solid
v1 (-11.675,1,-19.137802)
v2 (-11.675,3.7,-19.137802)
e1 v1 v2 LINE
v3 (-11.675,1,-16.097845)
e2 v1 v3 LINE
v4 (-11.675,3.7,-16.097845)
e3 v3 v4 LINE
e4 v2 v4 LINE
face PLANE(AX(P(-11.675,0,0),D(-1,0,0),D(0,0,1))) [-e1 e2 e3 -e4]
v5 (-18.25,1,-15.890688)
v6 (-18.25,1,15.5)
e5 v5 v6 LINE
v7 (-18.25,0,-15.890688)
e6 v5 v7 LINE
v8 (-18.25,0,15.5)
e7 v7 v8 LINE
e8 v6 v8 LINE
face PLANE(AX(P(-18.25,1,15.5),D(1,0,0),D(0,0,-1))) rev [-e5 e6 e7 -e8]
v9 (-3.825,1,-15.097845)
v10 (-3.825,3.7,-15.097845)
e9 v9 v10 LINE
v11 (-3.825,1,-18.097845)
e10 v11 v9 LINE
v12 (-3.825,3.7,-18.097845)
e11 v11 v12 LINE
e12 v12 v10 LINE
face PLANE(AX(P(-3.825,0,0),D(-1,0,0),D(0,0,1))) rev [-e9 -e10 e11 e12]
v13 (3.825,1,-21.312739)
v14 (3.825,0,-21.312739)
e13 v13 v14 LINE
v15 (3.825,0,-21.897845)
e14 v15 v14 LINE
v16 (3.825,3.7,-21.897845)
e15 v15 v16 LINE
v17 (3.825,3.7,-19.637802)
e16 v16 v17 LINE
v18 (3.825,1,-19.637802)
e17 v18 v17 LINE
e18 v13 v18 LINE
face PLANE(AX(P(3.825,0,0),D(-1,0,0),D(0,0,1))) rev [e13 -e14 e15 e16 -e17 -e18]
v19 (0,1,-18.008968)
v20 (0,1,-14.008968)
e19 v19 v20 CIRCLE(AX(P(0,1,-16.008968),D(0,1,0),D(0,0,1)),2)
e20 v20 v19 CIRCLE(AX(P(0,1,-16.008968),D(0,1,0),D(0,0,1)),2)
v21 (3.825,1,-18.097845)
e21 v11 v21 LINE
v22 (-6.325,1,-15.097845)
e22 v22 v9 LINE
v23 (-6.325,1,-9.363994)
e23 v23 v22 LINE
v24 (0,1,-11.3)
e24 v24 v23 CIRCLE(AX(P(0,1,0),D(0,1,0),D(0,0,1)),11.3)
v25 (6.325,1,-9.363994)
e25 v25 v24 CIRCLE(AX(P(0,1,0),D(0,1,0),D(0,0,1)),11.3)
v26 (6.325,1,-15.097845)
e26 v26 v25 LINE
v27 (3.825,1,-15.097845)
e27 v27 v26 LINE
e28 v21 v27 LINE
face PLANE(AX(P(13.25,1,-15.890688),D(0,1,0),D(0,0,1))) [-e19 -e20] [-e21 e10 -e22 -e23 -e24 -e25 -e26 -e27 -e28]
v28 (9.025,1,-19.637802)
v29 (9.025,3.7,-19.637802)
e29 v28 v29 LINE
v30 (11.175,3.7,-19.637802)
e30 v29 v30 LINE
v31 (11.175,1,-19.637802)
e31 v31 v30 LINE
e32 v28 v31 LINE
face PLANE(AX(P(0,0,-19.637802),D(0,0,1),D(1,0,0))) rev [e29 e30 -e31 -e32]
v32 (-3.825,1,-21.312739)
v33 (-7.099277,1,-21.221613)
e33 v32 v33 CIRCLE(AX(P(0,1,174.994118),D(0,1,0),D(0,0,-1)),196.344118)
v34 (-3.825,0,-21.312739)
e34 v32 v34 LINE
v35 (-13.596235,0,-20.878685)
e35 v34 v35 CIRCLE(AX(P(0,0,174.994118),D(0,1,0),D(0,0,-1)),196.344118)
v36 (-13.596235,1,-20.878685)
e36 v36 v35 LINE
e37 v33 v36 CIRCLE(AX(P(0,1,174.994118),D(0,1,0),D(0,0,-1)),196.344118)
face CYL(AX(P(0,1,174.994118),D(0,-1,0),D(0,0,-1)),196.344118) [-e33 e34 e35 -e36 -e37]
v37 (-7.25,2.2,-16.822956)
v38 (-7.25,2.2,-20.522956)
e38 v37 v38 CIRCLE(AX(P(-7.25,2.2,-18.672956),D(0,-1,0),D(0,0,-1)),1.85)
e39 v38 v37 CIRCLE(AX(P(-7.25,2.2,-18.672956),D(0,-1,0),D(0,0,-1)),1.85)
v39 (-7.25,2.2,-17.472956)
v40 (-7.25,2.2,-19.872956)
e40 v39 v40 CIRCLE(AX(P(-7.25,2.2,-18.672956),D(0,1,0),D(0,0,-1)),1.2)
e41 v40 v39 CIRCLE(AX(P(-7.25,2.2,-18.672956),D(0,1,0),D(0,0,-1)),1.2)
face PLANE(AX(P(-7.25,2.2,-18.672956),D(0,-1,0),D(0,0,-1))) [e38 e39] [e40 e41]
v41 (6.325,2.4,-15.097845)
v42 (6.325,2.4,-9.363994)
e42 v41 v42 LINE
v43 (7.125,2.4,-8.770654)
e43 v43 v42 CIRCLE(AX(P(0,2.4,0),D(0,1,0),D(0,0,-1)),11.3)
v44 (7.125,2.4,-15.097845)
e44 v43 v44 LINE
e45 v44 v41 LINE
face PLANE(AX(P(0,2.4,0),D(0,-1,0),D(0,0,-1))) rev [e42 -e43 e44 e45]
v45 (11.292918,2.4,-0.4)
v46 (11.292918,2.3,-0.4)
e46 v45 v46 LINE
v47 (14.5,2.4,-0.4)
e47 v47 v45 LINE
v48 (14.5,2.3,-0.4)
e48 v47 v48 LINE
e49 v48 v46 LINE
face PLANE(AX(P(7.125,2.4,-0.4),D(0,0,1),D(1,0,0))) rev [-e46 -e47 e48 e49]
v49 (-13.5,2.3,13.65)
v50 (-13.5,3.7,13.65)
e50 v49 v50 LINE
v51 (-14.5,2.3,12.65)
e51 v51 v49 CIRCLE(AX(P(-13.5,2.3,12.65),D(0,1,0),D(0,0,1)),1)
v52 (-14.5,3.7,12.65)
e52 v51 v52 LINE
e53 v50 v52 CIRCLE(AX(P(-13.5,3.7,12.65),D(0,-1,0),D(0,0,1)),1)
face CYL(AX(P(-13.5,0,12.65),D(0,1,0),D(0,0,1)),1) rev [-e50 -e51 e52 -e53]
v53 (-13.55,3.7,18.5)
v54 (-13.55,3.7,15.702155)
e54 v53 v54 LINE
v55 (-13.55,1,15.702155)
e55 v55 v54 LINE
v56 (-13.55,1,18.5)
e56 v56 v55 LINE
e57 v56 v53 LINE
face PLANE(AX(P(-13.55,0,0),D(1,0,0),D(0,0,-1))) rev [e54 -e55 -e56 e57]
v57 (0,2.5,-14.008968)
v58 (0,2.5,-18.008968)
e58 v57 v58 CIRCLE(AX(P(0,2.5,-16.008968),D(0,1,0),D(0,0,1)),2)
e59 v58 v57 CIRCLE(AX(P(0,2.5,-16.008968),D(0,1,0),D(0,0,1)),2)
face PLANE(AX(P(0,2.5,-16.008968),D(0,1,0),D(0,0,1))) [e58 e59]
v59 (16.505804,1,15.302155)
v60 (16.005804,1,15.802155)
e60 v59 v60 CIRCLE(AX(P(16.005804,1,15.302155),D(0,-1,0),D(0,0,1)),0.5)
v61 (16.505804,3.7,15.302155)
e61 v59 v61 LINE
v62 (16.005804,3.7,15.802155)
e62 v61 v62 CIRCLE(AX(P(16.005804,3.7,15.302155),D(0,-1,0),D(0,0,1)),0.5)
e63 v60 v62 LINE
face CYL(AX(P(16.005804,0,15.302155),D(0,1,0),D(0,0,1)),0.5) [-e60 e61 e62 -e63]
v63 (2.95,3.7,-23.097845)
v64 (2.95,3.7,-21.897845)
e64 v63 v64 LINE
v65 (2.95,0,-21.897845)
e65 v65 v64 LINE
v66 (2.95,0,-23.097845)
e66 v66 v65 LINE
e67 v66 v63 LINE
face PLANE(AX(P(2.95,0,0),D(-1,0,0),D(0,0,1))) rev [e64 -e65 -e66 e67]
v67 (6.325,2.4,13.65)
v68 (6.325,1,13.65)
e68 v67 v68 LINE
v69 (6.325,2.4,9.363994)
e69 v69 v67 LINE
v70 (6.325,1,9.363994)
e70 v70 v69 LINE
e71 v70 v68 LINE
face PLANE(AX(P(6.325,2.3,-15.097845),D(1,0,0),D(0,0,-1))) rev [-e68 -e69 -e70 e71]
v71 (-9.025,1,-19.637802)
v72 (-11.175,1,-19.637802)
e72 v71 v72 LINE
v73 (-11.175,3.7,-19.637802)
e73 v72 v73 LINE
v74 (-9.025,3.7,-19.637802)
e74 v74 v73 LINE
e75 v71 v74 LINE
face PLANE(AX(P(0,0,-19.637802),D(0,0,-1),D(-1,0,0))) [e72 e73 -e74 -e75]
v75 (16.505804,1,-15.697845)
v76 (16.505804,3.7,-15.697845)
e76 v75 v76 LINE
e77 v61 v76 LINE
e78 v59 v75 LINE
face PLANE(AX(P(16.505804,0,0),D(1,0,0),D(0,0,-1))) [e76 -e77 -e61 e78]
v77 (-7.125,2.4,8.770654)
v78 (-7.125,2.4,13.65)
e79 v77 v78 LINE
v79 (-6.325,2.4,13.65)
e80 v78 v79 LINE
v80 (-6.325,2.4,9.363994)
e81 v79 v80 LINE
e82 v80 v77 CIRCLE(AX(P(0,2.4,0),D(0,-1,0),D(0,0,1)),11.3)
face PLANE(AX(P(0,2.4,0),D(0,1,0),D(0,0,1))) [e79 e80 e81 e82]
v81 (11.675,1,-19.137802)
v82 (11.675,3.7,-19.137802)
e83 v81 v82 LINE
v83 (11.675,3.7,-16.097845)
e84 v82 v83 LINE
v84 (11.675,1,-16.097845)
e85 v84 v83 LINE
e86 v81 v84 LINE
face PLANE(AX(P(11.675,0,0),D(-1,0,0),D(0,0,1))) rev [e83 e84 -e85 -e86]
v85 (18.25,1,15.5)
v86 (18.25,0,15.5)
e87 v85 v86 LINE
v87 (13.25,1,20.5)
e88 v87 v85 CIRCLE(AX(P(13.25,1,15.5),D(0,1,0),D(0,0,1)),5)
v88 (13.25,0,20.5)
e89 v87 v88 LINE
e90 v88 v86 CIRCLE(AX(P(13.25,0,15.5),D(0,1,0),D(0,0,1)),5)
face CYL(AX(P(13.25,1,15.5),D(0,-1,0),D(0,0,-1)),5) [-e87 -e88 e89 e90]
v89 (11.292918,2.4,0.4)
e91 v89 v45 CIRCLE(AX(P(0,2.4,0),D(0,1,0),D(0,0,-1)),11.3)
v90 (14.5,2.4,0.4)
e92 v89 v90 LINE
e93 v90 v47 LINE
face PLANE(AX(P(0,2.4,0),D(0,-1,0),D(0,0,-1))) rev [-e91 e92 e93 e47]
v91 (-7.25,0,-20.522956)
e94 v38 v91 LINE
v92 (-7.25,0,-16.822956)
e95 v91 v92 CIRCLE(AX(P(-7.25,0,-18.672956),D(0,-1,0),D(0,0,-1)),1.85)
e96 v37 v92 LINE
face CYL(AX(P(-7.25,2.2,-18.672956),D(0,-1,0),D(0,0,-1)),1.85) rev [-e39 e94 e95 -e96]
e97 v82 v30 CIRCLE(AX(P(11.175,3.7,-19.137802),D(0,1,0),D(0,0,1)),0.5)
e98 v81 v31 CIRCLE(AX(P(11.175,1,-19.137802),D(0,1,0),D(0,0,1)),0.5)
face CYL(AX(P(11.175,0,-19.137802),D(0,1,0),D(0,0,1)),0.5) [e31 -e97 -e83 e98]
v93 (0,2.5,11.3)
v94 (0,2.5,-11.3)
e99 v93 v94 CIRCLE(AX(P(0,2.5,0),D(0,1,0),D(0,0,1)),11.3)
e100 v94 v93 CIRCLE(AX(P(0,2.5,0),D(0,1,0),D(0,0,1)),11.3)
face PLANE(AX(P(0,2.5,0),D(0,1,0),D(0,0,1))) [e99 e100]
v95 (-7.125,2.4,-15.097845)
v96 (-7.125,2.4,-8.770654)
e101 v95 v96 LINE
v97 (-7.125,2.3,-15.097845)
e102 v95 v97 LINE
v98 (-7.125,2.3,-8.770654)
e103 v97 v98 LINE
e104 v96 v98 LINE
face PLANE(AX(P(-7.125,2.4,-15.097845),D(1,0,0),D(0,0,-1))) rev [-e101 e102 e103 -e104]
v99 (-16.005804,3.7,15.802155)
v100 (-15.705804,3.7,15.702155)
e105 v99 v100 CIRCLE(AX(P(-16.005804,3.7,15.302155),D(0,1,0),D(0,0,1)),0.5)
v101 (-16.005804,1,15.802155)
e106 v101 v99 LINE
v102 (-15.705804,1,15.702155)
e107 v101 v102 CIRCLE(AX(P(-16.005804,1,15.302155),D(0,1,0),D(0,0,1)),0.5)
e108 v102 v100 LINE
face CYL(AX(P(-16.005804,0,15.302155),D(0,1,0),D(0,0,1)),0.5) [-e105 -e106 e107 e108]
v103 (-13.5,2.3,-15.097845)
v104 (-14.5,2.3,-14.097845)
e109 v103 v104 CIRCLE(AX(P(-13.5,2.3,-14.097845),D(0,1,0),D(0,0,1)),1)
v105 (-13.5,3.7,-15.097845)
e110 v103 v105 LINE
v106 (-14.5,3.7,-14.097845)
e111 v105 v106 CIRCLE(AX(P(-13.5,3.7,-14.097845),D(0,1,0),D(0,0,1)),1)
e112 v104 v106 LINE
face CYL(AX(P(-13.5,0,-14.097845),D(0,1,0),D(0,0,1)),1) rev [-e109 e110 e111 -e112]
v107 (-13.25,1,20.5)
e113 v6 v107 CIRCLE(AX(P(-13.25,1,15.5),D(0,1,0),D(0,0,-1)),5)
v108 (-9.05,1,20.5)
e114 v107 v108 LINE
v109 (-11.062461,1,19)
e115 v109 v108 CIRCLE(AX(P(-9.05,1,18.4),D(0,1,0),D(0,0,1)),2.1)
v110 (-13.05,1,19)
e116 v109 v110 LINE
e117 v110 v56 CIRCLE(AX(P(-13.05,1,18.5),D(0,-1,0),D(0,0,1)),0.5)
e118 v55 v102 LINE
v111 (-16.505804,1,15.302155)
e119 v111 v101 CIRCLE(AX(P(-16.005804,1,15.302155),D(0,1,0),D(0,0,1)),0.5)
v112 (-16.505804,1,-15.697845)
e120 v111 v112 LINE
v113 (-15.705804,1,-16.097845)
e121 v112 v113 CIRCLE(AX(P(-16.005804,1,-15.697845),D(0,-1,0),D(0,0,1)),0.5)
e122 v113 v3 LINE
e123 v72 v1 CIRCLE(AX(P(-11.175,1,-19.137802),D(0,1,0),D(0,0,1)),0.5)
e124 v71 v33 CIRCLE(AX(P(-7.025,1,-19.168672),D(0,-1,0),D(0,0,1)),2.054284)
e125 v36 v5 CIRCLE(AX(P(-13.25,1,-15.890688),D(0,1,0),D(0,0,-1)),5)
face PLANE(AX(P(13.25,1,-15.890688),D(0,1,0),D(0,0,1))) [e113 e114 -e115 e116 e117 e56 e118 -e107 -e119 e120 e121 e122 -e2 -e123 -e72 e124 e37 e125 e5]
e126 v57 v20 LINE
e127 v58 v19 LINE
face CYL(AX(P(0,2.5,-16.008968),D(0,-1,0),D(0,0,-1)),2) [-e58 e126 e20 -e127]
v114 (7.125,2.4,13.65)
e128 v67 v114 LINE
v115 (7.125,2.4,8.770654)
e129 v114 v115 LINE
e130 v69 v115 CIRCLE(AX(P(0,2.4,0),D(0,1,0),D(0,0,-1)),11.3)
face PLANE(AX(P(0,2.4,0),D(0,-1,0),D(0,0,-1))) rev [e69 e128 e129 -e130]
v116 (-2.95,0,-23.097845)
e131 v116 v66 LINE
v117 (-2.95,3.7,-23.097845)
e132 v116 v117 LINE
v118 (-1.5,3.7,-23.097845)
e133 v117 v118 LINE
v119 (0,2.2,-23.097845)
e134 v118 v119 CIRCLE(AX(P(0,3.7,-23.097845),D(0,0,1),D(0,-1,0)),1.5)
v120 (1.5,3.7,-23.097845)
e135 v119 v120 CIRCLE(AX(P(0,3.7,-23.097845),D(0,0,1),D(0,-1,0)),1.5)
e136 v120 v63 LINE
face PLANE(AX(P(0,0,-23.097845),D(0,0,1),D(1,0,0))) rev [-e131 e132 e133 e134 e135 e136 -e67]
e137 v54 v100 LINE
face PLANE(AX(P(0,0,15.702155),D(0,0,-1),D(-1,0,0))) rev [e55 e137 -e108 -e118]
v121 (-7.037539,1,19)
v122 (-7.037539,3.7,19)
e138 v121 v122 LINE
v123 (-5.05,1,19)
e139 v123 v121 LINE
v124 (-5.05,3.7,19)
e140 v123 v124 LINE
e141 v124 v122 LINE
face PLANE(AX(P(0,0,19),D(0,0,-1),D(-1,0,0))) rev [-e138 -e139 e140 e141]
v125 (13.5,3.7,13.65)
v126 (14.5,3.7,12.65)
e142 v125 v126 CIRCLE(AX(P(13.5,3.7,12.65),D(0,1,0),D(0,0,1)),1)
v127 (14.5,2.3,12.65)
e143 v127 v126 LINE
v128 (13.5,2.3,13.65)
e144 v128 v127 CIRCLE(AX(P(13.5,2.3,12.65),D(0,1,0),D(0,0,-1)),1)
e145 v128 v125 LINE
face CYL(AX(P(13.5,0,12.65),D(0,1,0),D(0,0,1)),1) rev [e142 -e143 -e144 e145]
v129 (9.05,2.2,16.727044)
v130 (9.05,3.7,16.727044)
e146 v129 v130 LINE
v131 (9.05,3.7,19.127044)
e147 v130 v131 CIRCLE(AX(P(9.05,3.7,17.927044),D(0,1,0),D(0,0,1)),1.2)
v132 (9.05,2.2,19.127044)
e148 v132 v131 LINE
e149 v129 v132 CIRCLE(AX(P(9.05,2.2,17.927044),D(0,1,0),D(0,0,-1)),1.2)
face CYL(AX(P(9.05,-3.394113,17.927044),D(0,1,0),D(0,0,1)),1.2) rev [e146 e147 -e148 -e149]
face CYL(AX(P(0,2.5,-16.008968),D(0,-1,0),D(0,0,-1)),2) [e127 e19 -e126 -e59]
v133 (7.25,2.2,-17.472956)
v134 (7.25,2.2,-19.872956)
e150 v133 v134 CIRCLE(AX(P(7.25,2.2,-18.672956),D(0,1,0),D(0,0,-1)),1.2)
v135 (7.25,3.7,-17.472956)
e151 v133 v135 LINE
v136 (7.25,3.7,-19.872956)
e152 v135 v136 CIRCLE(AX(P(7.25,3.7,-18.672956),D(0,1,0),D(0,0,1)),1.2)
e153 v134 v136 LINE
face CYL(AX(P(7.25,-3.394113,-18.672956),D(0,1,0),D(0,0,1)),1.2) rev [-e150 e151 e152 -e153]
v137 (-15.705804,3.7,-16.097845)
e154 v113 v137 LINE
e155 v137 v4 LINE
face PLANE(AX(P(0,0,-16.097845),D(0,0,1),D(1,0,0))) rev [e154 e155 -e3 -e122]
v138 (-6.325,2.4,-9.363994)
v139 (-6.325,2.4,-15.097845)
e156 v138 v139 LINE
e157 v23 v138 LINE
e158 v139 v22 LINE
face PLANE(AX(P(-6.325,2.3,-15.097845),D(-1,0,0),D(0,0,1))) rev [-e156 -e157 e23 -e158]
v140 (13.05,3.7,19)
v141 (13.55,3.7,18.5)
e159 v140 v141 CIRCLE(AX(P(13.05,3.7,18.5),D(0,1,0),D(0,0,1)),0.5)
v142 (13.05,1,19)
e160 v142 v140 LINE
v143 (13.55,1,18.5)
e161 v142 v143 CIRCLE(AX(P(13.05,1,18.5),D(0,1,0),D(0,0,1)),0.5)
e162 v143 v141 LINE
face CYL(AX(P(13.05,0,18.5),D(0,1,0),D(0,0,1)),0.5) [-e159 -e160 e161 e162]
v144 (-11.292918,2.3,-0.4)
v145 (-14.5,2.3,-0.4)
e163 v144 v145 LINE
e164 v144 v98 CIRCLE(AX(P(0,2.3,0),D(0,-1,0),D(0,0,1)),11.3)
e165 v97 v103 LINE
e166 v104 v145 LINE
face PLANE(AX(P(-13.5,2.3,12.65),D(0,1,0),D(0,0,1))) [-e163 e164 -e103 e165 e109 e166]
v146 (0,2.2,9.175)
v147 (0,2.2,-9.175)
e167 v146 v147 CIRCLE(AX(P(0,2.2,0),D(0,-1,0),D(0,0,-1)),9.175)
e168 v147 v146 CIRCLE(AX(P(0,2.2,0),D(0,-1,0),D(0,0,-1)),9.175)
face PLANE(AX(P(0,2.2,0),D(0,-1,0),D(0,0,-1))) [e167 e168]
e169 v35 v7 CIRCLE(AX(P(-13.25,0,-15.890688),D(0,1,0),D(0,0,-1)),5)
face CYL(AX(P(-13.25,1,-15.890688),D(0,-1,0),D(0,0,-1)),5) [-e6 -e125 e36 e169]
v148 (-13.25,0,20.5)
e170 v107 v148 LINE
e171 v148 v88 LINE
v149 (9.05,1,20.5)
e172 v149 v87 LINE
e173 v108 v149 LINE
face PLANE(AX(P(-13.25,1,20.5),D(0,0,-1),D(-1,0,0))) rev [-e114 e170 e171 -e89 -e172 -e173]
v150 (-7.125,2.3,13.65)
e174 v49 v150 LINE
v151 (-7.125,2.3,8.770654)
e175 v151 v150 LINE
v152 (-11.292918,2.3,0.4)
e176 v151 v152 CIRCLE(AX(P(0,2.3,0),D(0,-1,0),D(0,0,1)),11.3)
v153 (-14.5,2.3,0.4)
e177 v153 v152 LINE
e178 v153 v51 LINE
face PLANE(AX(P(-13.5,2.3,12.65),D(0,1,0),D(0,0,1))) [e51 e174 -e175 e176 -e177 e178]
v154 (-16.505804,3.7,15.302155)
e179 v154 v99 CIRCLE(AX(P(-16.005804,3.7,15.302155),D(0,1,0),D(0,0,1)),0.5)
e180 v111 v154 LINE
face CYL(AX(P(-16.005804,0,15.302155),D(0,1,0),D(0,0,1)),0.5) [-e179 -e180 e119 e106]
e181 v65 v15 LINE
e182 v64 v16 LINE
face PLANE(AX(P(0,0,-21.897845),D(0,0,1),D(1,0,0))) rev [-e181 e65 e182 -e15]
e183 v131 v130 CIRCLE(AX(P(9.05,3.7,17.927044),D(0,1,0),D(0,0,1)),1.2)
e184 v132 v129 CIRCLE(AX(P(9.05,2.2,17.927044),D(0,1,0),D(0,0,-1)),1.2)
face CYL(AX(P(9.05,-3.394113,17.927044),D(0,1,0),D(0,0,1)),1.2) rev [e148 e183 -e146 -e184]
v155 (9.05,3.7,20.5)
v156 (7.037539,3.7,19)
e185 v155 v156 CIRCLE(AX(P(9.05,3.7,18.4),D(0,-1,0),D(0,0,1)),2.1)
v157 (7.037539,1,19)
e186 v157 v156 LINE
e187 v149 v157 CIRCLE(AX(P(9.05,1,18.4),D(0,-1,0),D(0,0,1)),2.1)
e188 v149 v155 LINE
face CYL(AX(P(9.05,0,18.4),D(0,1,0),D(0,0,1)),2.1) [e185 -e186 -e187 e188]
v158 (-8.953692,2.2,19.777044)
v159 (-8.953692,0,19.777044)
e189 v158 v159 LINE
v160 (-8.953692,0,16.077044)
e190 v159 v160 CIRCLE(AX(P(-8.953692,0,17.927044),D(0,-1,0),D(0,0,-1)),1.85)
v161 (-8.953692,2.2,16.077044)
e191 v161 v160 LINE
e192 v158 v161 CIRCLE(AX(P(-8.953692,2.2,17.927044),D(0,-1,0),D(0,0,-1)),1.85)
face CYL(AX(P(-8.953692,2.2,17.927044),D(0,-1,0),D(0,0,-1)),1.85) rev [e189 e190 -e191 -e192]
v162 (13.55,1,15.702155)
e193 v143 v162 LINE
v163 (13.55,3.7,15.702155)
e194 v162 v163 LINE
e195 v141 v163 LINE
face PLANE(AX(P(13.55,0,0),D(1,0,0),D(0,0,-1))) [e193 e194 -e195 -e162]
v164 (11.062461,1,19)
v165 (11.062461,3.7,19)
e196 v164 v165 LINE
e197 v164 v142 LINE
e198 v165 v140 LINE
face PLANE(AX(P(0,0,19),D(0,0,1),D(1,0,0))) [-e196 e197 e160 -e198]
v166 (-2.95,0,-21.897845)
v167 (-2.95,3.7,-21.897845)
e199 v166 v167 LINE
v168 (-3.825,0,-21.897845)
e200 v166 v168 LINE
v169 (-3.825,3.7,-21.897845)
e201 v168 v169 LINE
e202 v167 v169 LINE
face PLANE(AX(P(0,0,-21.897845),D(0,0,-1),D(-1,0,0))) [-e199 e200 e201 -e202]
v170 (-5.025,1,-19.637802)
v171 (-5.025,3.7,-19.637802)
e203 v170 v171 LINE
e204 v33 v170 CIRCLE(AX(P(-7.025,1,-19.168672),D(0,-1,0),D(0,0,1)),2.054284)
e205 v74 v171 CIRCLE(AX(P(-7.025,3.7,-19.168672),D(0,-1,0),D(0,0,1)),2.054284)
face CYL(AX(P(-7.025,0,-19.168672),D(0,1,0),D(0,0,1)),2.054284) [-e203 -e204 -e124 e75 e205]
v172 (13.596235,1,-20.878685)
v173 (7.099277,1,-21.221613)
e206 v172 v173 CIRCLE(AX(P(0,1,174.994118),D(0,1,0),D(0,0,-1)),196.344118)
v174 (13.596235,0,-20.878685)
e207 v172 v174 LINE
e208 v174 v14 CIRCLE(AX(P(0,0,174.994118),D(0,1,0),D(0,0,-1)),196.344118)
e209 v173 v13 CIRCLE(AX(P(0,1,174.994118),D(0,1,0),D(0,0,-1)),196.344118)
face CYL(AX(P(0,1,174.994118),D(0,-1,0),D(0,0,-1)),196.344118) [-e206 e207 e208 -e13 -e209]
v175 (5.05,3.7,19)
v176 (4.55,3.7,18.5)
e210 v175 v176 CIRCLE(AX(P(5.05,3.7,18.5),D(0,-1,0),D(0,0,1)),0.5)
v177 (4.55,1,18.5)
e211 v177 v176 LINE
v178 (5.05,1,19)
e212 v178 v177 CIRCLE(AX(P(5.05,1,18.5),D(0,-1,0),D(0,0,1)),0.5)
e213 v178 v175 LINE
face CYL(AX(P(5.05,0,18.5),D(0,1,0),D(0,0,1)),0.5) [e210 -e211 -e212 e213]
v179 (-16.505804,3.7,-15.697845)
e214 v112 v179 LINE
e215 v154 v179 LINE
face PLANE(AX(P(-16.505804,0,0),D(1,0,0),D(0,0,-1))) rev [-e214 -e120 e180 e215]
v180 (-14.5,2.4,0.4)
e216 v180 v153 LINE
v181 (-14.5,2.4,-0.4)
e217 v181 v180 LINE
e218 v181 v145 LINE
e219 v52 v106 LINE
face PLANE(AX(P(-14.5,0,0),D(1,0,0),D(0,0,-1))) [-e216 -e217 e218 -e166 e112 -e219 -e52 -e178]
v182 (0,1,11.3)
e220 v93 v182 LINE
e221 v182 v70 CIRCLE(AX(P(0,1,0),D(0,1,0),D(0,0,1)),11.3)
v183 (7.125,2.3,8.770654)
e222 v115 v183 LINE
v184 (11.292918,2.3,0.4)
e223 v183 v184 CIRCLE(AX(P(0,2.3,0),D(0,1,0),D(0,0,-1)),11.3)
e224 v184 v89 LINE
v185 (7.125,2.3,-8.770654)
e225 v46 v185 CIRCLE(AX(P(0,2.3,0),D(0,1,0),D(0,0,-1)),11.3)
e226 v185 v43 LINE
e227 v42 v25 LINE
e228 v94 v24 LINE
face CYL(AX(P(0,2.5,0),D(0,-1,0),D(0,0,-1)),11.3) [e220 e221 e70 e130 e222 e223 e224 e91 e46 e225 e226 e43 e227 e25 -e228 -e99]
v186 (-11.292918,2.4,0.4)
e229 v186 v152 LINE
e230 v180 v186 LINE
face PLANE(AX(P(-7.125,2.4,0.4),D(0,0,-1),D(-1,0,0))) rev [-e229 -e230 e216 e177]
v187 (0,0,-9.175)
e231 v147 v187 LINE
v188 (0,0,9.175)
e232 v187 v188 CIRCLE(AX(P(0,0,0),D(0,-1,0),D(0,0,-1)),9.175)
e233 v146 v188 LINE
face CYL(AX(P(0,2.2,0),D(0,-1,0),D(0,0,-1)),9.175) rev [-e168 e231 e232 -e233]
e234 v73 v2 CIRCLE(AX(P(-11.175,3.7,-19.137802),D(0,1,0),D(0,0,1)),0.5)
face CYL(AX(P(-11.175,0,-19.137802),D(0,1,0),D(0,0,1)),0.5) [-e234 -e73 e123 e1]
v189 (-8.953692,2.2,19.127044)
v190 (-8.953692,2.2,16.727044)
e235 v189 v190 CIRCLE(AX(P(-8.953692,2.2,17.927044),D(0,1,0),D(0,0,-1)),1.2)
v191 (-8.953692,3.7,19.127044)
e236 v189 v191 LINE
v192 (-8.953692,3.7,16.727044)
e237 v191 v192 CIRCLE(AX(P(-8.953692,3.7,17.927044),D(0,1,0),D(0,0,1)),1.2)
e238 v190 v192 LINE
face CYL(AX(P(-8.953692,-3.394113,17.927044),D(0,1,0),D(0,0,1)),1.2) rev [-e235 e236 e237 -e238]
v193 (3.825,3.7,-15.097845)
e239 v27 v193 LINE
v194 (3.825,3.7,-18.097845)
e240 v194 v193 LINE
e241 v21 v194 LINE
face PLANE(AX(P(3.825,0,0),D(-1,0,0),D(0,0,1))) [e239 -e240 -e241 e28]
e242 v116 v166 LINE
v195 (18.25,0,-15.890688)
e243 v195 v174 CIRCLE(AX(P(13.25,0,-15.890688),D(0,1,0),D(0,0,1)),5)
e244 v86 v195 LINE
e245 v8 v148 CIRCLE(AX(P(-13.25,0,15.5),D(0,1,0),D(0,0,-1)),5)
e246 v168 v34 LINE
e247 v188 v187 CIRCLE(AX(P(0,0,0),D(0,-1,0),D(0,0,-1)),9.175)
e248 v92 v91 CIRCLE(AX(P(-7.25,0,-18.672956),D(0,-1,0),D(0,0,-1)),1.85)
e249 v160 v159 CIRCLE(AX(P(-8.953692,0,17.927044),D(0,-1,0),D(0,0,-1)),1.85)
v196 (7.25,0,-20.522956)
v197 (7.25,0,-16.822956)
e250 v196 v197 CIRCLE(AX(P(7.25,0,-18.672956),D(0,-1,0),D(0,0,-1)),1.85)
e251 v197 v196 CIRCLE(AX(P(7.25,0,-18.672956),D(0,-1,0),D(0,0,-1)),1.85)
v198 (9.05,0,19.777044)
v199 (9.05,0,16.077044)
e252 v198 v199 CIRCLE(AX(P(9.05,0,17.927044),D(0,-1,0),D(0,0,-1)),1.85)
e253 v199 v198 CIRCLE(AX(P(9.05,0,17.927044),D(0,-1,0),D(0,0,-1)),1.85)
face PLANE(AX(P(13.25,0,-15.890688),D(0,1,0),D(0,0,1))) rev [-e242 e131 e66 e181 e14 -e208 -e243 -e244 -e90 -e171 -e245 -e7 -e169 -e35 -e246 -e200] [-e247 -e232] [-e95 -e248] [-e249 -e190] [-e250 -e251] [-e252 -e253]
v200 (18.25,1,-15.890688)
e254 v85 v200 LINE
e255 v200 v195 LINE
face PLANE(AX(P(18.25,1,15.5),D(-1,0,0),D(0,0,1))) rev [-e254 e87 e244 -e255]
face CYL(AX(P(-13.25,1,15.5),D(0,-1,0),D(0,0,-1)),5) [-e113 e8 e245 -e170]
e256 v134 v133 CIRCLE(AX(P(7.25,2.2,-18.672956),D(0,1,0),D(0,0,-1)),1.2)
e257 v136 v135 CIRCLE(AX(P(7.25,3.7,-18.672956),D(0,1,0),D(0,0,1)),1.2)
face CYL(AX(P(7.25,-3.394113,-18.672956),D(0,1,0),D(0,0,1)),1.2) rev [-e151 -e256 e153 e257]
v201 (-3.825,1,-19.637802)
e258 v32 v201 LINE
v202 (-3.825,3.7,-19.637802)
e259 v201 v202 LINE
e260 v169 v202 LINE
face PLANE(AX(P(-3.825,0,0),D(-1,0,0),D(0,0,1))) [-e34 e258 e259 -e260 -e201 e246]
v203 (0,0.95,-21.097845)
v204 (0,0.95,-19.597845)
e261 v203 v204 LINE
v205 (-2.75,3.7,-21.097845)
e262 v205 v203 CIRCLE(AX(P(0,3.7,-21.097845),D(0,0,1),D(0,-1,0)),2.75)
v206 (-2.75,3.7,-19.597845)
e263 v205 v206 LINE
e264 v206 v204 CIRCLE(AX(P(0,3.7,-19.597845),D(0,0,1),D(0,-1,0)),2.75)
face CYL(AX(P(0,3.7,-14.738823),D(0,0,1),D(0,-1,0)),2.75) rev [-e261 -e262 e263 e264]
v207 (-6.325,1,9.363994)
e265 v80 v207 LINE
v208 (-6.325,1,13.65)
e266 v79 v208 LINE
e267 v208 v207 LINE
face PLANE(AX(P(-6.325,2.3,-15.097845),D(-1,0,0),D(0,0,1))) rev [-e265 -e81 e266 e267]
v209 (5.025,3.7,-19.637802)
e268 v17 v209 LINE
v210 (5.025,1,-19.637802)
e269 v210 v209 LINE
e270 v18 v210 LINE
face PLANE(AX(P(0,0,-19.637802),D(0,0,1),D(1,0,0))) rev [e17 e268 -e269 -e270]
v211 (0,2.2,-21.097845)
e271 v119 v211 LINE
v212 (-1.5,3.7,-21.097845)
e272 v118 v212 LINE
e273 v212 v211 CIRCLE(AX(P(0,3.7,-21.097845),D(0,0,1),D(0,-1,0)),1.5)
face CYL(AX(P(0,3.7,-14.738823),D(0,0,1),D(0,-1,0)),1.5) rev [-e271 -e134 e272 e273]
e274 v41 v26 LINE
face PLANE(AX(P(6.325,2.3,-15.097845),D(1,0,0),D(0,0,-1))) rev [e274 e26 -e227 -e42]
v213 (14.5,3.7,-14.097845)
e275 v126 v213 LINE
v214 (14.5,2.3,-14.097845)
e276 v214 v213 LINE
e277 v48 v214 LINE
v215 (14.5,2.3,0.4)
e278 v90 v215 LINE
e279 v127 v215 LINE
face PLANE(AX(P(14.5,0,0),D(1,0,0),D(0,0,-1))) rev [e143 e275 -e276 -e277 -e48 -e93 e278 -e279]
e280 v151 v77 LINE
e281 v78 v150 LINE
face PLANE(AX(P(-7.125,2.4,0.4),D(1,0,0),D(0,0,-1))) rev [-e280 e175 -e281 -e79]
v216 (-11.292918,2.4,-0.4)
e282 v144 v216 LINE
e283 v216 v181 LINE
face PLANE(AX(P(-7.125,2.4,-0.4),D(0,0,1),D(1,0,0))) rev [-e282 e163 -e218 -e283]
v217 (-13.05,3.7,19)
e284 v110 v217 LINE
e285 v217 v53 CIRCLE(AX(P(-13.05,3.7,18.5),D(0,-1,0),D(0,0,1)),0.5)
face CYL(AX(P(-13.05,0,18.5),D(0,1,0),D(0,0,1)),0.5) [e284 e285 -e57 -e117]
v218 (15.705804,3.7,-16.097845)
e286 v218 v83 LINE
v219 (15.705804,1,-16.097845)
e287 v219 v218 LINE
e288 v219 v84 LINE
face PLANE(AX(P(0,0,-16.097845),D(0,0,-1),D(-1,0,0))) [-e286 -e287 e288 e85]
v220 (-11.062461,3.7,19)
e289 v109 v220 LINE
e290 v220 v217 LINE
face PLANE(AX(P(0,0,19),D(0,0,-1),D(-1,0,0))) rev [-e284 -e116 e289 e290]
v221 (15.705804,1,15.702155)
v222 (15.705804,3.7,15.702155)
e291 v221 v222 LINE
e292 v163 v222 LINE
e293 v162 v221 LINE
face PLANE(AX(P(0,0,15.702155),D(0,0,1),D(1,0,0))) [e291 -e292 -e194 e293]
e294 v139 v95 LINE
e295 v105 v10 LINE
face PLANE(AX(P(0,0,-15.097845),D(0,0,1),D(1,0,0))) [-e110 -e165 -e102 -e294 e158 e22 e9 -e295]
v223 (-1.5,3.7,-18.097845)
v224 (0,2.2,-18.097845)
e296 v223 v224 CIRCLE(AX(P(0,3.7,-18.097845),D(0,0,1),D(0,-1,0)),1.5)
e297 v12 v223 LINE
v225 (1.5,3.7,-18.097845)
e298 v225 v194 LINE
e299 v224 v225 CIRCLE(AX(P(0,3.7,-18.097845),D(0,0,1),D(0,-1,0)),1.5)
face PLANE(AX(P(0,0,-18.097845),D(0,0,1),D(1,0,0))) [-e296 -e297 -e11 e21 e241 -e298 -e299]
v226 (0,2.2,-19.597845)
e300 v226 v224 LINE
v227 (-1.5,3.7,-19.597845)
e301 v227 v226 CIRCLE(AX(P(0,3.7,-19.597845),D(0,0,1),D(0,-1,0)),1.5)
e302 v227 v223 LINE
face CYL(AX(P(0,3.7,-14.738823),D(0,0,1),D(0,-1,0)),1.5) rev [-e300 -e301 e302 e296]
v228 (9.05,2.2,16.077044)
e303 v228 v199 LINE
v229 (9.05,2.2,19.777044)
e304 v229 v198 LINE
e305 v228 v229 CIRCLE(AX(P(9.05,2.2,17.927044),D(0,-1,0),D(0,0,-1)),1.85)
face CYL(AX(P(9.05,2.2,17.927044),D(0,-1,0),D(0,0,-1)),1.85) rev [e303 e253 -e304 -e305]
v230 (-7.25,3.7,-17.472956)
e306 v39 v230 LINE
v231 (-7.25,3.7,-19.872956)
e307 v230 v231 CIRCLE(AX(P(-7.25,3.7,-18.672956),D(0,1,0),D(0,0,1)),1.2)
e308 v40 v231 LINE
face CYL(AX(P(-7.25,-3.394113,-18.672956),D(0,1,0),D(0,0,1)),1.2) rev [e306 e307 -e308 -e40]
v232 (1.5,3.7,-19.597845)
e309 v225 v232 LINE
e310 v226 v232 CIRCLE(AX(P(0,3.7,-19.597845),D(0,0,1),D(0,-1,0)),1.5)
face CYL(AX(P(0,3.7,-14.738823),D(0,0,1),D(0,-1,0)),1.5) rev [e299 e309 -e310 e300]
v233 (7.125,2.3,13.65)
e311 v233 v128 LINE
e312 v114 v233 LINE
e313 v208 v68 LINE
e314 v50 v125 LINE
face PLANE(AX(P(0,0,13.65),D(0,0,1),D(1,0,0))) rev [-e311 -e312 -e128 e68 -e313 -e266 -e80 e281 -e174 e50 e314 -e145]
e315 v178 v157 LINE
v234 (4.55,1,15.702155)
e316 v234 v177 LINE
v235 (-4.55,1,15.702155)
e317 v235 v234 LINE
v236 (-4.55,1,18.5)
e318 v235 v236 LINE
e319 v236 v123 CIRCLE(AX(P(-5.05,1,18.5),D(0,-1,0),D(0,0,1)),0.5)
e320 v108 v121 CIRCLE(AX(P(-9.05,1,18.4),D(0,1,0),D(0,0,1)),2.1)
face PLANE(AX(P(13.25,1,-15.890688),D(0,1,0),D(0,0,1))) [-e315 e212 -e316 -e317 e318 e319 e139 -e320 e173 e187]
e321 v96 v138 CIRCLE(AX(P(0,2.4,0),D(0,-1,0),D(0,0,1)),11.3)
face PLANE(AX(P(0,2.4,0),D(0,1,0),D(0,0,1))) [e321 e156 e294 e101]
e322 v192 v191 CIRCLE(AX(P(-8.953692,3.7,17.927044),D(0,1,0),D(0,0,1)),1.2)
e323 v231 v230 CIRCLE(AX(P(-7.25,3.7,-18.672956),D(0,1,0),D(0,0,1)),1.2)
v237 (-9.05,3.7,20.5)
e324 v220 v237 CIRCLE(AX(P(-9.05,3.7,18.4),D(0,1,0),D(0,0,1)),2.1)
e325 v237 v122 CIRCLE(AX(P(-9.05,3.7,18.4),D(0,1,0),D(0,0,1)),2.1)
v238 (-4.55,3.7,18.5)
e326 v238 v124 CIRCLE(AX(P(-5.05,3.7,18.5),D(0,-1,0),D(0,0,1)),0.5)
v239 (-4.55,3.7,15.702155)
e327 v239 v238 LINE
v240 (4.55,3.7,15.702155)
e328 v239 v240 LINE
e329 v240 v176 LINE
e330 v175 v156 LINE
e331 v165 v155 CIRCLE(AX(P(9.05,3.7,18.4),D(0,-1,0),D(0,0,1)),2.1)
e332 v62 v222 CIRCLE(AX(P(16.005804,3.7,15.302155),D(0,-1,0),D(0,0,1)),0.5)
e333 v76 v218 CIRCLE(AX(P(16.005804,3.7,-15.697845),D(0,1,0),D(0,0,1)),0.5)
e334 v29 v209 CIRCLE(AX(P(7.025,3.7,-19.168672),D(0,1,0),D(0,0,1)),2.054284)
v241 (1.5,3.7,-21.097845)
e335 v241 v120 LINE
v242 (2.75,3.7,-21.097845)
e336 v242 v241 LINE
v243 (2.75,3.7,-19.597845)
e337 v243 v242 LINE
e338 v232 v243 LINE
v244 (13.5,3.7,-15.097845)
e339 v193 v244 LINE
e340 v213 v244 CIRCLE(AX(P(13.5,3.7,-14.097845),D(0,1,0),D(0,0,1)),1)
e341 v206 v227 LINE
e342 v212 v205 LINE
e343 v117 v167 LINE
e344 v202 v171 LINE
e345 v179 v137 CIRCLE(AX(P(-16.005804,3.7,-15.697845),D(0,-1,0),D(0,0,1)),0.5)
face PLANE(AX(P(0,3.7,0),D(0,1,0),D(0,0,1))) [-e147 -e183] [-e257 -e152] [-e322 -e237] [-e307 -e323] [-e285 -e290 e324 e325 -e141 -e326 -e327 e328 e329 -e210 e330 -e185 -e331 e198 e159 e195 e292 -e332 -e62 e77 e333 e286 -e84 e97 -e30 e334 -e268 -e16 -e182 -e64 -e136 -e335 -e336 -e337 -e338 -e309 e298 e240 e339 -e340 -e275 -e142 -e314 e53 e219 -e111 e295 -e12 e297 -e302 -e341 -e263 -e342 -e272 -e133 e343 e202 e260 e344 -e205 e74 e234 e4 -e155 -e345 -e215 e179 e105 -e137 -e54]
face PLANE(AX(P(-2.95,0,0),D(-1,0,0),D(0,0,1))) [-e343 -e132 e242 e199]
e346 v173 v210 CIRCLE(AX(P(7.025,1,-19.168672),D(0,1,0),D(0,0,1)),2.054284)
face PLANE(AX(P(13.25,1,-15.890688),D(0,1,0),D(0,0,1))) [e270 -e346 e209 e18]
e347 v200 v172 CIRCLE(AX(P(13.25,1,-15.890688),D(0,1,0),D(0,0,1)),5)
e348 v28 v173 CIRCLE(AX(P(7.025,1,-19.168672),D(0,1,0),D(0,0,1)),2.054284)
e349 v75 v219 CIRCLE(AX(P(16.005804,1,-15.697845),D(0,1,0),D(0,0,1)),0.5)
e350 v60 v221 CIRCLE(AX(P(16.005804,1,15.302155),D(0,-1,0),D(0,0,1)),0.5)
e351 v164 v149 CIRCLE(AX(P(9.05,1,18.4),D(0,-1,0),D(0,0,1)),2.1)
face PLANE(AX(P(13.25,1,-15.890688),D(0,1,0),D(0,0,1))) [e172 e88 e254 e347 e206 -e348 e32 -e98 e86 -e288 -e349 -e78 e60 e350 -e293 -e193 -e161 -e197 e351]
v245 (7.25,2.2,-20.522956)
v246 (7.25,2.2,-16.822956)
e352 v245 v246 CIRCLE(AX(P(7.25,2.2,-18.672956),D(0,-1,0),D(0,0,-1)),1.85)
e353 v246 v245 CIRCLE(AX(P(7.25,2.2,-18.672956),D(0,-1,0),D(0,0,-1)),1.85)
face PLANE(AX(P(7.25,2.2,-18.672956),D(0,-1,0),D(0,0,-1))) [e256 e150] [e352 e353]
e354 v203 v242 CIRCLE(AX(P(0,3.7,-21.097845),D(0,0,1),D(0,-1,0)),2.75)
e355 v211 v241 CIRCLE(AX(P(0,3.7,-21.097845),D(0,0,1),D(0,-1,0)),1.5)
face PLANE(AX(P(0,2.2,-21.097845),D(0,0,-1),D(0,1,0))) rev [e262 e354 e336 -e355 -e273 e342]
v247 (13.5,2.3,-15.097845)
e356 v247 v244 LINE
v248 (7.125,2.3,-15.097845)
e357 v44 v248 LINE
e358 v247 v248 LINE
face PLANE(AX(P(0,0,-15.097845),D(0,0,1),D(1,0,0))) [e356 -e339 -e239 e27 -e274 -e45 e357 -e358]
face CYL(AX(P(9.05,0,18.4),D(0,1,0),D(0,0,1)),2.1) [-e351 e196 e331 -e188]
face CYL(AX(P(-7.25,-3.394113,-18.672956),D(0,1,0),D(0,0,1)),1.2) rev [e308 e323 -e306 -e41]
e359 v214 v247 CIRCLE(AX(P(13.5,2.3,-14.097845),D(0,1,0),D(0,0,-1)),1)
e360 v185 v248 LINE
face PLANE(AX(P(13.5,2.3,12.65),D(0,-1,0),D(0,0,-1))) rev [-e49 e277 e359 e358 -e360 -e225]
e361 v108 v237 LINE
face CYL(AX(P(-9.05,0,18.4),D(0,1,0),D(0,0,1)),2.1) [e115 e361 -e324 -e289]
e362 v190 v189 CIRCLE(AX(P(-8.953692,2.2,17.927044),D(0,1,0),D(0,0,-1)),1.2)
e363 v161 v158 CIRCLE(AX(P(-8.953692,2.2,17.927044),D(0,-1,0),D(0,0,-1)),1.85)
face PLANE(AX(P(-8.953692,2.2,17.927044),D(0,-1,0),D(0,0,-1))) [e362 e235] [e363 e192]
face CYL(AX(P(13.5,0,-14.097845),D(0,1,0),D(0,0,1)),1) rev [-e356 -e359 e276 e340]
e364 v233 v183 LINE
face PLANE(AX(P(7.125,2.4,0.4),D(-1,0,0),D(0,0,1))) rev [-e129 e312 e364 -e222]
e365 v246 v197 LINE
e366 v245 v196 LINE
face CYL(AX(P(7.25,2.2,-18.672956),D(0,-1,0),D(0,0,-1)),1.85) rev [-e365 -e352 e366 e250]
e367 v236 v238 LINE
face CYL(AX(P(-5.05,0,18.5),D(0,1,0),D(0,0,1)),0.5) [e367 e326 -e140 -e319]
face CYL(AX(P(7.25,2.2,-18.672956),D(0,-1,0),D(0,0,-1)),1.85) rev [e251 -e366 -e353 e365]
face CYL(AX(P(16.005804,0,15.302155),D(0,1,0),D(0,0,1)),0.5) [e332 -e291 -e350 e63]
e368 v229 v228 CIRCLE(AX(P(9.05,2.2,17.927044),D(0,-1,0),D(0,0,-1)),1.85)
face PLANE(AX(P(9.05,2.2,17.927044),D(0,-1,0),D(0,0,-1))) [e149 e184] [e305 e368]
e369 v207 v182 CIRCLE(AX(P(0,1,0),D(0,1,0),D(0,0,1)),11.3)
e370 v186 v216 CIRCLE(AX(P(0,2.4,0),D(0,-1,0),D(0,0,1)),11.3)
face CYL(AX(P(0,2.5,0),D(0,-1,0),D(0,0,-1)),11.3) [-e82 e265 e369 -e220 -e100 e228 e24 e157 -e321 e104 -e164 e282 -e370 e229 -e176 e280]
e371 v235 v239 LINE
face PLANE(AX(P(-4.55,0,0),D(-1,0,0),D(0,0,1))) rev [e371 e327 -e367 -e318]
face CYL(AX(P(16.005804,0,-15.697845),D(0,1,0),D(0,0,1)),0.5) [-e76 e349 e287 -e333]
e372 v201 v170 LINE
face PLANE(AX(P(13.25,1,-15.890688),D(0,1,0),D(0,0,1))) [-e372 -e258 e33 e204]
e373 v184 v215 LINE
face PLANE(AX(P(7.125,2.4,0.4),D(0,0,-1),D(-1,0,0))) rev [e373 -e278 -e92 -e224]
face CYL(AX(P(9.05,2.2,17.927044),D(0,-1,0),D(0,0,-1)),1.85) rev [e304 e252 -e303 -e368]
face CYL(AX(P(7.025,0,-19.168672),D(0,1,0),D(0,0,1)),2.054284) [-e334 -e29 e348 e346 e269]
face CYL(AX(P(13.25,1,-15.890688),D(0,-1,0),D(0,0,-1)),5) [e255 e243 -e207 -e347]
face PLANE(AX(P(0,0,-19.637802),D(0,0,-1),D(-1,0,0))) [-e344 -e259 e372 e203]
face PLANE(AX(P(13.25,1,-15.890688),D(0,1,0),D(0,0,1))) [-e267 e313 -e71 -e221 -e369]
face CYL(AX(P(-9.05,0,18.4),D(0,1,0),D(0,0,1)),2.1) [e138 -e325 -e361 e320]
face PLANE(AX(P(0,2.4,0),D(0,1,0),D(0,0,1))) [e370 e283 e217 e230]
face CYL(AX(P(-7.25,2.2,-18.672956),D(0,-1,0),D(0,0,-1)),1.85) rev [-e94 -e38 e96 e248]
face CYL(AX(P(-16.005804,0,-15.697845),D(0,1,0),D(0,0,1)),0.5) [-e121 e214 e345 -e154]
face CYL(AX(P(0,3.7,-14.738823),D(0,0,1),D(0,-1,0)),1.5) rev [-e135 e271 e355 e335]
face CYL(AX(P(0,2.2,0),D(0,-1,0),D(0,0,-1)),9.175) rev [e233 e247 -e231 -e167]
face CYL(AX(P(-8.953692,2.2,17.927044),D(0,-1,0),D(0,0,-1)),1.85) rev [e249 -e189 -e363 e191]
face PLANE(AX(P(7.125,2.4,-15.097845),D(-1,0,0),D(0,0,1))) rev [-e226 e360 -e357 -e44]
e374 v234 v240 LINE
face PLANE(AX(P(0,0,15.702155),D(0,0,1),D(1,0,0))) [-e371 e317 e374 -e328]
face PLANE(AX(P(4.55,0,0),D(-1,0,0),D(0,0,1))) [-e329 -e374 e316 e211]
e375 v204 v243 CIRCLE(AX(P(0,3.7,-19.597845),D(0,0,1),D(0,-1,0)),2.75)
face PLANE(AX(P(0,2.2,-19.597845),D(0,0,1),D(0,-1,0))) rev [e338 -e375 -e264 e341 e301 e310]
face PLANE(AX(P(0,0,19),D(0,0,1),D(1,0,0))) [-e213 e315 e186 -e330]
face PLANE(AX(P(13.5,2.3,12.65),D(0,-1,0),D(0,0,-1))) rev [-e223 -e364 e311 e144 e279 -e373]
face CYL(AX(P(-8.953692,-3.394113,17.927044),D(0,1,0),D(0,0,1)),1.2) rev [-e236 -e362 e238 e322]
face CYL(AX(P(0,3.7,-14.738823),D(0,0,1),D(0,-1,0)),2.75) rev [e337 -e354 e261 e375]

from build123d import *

# Parameters (mm, degrees)
BOSS_EXTRUDE1_DEPTH      = 1
BOSS_EXTRUDE3_DEPTH      = 2.7
BOSS_EXTRUDE3_DEPTH_BACK = 1
BOSS_EXTRUDE4_DEPTH      = 1.3
BOSS_EXTRUDE5_DEPTH      = 0.1
SKETCH_6_R               = 11.3
BOSS_EXTRUDE6_DEPTH      = 1.5
SKETCH_8_R               = 1.2
CUT_EXTRUDE1_DEPTH       = 3.7
SKETCH_9_R               = 1.85
SKETCH_9_R_2             = 9.175
CUT_EXTRUDE2_DEPTH       = 2.2
SKETCH_10_R              = 2
BOSS_EXTRUDE11_DEPTH     = 1.5


with BuildPart() as part:
    # Sketch 1 → Boss-Extrude1 (new body)
    with BuildSketch(Plane(origin=(0, 0, 0), x_dir=(1, 0, 0), z_dir=(0, 1, 0))):
        with BuildLine():
            Line((-13.25, -20.5), (13.25, -20.5))
            ThreePointArc((13.25, -20.5), (16.785533906, -19.035533906), (18.25, -15.5))
            Line((18.25, -15.5), (18.25, 15.890687558))
            ThreePointArc((18.25, 15.890687558), (16.905897578, 19.301613077), (13.59623484, 20.878685296))
            ThreePointArc((13.59623484, 20.878685296), (0, 21.35), (-13.59623484, 20.878685296))
            ThreePointArc((-13.59623484, 20.878685296), (-16.905897578, 19.301613077), (-18.25, 15.890687558))
            Line((-18.25, 15.890687558), (-18.25, -15.5))
            ThreePointArc((-18.25, -15.5), (-16.785533906, -19.035533906), (-13.25, -20.5))
        make_face()
    extrude(amount=BOSS_EXTRUDE1_DEPTH)

    # Sketch 2 → Boss-Extrude3 (add, two sides: drawn at the far end of the back side and taken through both)
    with BuildSketch(Plane(origin=(0, 1, 0), x_dir=(1, 0, 0), z_dir=(0, 1, 0)).offset(-BOSS_EXTRUDE3_DEPTH_BACK)):
        with BuildLine():
            Line((-13.55, -15.702154728), (-15.705804316, -15.702154728))
            ThreePointArc((-15.705804316, -15.702154728), (-16.229411113, -15.749368323), (-16.505804316, -15.302154728))
            Line((-16.505804316, -15.302154728), (-16.505804316, 15.697845272))
            ThreePointArc((-16.505804316, 15.697845272), (-16.229411113, 16.145058868), (-15.705804316, 16.097845272))
            Line((-15.705804316, 16.097845272), (-11.675, 16.097845272))
            Line((-11.675, 16.097845272), (-11.675, 19.137801572))
            ThreePointArc((-11.675, 19.137801572), (-11.528553391, 19.491354963), (-11.175, 19.637801572))
            Line((-11.175, 19.637801572), (-9.025, 19.637801572))
            ThreePointArc((-9.025, 19.637801572), (-7.025, 21.222955871), (-5.025, 19.637801572))
            Line((-5.025, 19.637801572), (-3.825, 19.637801572))
            Line((-3.825, 19.637801572), (-3.825, 21.897845272))
            Line((-3.825, 21.897845272), (-2.95, 21.897845272))
            Line((-2.95, 21.897845272), (-2.95, 23.097845272))
            Line((-2.95, 23.097845272), (2.95, 23.097845272))
            Line((2.95, 23.097845272), (2.95, 21.897845272))
            Line((2.95, 21.897845272), (3.825, 21.897845272))
            Line((3.825, 21.897845272), (3.825, 19.637801572))
            Line((3.825, 19.637801572), (5.025, 19.637801572))
            ThreePointArc((5.025, 19.637801572), (7.025, 21.222955871), (9.025, 19.637801572))
            Line((9.025, 19.637801572), (11.175, 19.637801572))
            ThreePointArc((11.175, 19.637801572), (11.528553391, 19.491354963), (11.675, 19.137801572))
            Line((11.675, 19.137801572), (11.675, 16.097845272))
            Line((11.675, 16.097845272), (15.705804316, 16.097845272))
            ThreePointArc((15.705804316, 16.097845272), (16.229411113, 16.145058868), (16.505804316, 15.697845272))
            Line((16.505804316, 15.697845272), (16.505804316, -15.302154728))
            ThreePointArc((16.505804316, -15.302154728), (16.229411113, -15.749368323), (15.705804316, -15.702154728))
            Line((15.705804316, -15.702154728), (13.55, -15.702154728))
            Line((13.55, -15.702154728), (13.55, -18.5))
            ThreePointArc((13.55, -18.5), (13.403553391, -18.853553391), (13.05, -19))
            Line((13.05, -19), (11.06246118, -19))
            ThreePointArc((11.06246118, -19), (9.05, -20.5), (7.03753882, -19))
            Line((7.03753882, -19), (5.05, -19))
            ThreePointArc((5.05, -19), (4.696446609, -18.853553391), (4.55, -18.5))
            Line((4.55, -18.5), (4.55, -15.702154728))
            Line((4.55, -15.702154728), (-4.55, -15.702154728))
            Line((-4.55, -15.702154728), (-4.55, -18.5))
            ThreePointArc((-4.55, -18.5), (-4.696446609, -18.853553391), (-5.05, -19))
            Line((-5.05, -19), (-7.03753882, -19))
            ThreePointArc((-7.03753882, -19), (-9.05, -20.5), (-11.06246118, -19))
            Line((-11.06246118, -19), (-13.05, -19))
            ThreePointArc((-13.05, -19), (-13.403553391, -18.853553391), (-13.55, -18.5))
            Line((-13.55, -18.5), (-13.55, -15.702154728))
        make_face()
        with BuildLine():
            Line((-14.5, -12.65), (-14.5, 14.097845272))
            ThreePointArc((-14.5, 14.097845272), (-14.207106781, 14.804952053), (-13.5, 15.097845272))
            Line((-13.5, 15.097845272), (-3.825, 15.097845272))
            Line((-3.825, 15.097845272), (-3.825, 18.097845272))
            Line((-3.825, 18.097845272), (3.825, 18.097845272))
            Line((3.825, 18.097845272), (3.825, 15.097845272))
            Line((3.825, 15.097845272), (13.5, 15.097845272))
            ThreePointArc((13.5, 15.097845272), (14.207106781, 14.804952053), (14.5, 14.097845272))
            Line((14.5, 14.097845272), (14.5, -12.65))
            ThreePointArc((14.5, -12.65), (14.207106781, -13.357106781), (13.5, -13.65))
            Line((13.5, -13.65), (-13.5, -13.65))
            ThreePointArc((-13.5, -13.65), (-14.207106781, -13.357106781), (-14.5, -12.65))
        make_face(mode=Mode.SUBTRACT)
    extrude(amount=BOSS_EXTRUDE3_DEPTH + BOSS_EXTRUDE3_DEPTH_BACK)

    # Sketch 4 → Boss-Extrude4 (add)
    with BuildSketch(Plane(origin=(0, 1, 0), x_dir=(1, 0, 0), z_dir=(0, 1, 0))):
        with BuildLine():
            Line((-6.325, 15.097845272), (-6.325, -13.65))
            Line((-6.325, -13.65), (-13.5, -13.65))
            ThreePointArc((-13.5, -13.65), (-14.207106781, -13.357106781), (-14.5, -12.65))
            Line((-14.5, -12.65), (-14.5, 14.097845272))
            ThreePointArc((-14.5, 14.097845272), (-14.207106781, 14.804952053), (-13.5, 15.097845272))
            Line((-13.5, 15.097845272), (-6.325, 15.097845272))
        make_face()
        with BuildLine():
            Line((13.5, -13.65), (6.325, -13.65))
            Line((6.325, -13.65), (6.325, 15.097845272))
            Line((6.325, 15.097845272), (13.5, 15.097845272))
            ThreePointArc((13.5, 15.097845272), (14.207106781, 14.804952053), (14.5, 14.097845272))
            Line((14.5, 14.097845272), (14.5, -12.65))
            ThreePointArc((14.5, -12.65), (14.207106781, -13.357106781), (13.5, -13.65))
        make_face()
    extrude(amount=BOSS_EXTRUDE4_DEPTH)

    # Sketch 5 → Boss-Extrude5 (add)
    with BuildSketch(Plane(origin=(0, 2.3, 0), x_dir=(1, 0, 0), z_dir=(0, 1, 0))):
        Polygon((-6.325, 15.097845272), (-6.325, -13.65), (-7.125, -13.65), (-7.125, -0.4), (-14.5, -0.4), (-14.5, 0.4), (-7.125, 0.4), (-7.125, 15.097845272), align=None)
        Polygon((7.125, -0.4), (7.125, -13.65), (6.325, -13.65), (6.325, 15.097845272), (7.125, 15.097845272), (7.125, 0.4), (14.5, 0.4), (14.5, -0.4), align=None)
    extrude(amount=BOSS_EXTRUDE5_DEPTH)

    # Sketch 6 → Boss-Extrude6 (add)
    with BuildSketch(Plane(origin=(0, 1, 0), x_dir=(1, 0, 0), z_dir=(0, 1, 0))):
        with Locations(Location((0, 0, 0), (0, 0, 55.962560444))):
            Circle(SKETCH_6_R)
    extrude(amount=BOSS_EXTRUDE6_DEPTH)

    # Sketch 7 → Cut-Revolve1 (revolve, cut)
    with BuildSketch(Plane(origin=(0, 0, 0), x_dir=(0, 0, -1), z_dir=(1, 0, 0))):
        Polygon((23.097845272, 3.7), (23.097845272, 2.2), (21.097845272, 2.2), (21.097845272, 0.95), (19.597845272, 0.95), (19.597845272, 2.2), (18.097845272, 2.2), (18.097845272, 3.7), align=None)
    revolve(axis=Axis((0, 3.7, -14.738823172), (0, 0, -1)), mode=Mode.SUBTRACT)

    # Sketch 8 → Cut-Extrude1 (cut)
    with BuildSketch(Plane(origin=(0, 3.7, 0), x_dir=(1, 0, 0), z_dir=(0, 1, 0))):
        with Locations(Location((-7.25, 18.672955871, 0), (0, 0, 270))):
            Circle(SKETCH_8_R)
        with Locations(Location((9.05, -17.927044129, 0), (0, 0, 270))):
            Circle(SKETCH_8_R)
        with Locations(Location((-8.953692371, -17.927044129, 0), (0, 0, 270))):
            Circle(SKETCH_8_R)
        with Locations(Location((7.25, 18.672955871, 0), (0, 0, 270))):
            Circle(SKETCH_8_R)
    extrude(amount=-CUT_EXTRUDE1_DEPTH, mode=Mode.SUBTRACT)

    # Sketch 9 → Cut-Extrude2 (cut)
    with BuildSketch(Plane.XZ):
        with Locations(Location((-8.953692371, 17.927044129, 0), (0, 0, 270))):
            Circle(SKETCH_9_R)
        with Locations(Location((9.05, 17.927044129, 0), (0, 0, 270))):
            Circle(SKETCH_9_R)
        with Locations(Location((-7.25, -18.672955871, 0), (0, 0, 270))):
            Circle(SKETCH_9_R)
        with Locations(Location((7.25, -18.672955871, 0), (0, 0, 270))):
            Circle(SKETCH_9_R)
        with Locations(Location((0, 0, 0), (0, 0, 270))):
            Circle(SKETCH_9_R_2)
    extrude(amount=-CUT_EXTRUDE2_DEPTH, mode=Mode.SUBTRACT)

    # Sketch 10 → Boss-Extrude11 (add)
    with BuildSketch(Plane(origin=(0, 1, 0), x_dir=(1, 0, 0), z_dir=(0, 1, 0))):
        with Locations(Location((0, 16.008968339, 0), (0, 0, 270))):
            Circle(SKETCH_10_R)
    extrude(amount=BOSS_EXTRUDE11_DEPTH)


solid = part.part
